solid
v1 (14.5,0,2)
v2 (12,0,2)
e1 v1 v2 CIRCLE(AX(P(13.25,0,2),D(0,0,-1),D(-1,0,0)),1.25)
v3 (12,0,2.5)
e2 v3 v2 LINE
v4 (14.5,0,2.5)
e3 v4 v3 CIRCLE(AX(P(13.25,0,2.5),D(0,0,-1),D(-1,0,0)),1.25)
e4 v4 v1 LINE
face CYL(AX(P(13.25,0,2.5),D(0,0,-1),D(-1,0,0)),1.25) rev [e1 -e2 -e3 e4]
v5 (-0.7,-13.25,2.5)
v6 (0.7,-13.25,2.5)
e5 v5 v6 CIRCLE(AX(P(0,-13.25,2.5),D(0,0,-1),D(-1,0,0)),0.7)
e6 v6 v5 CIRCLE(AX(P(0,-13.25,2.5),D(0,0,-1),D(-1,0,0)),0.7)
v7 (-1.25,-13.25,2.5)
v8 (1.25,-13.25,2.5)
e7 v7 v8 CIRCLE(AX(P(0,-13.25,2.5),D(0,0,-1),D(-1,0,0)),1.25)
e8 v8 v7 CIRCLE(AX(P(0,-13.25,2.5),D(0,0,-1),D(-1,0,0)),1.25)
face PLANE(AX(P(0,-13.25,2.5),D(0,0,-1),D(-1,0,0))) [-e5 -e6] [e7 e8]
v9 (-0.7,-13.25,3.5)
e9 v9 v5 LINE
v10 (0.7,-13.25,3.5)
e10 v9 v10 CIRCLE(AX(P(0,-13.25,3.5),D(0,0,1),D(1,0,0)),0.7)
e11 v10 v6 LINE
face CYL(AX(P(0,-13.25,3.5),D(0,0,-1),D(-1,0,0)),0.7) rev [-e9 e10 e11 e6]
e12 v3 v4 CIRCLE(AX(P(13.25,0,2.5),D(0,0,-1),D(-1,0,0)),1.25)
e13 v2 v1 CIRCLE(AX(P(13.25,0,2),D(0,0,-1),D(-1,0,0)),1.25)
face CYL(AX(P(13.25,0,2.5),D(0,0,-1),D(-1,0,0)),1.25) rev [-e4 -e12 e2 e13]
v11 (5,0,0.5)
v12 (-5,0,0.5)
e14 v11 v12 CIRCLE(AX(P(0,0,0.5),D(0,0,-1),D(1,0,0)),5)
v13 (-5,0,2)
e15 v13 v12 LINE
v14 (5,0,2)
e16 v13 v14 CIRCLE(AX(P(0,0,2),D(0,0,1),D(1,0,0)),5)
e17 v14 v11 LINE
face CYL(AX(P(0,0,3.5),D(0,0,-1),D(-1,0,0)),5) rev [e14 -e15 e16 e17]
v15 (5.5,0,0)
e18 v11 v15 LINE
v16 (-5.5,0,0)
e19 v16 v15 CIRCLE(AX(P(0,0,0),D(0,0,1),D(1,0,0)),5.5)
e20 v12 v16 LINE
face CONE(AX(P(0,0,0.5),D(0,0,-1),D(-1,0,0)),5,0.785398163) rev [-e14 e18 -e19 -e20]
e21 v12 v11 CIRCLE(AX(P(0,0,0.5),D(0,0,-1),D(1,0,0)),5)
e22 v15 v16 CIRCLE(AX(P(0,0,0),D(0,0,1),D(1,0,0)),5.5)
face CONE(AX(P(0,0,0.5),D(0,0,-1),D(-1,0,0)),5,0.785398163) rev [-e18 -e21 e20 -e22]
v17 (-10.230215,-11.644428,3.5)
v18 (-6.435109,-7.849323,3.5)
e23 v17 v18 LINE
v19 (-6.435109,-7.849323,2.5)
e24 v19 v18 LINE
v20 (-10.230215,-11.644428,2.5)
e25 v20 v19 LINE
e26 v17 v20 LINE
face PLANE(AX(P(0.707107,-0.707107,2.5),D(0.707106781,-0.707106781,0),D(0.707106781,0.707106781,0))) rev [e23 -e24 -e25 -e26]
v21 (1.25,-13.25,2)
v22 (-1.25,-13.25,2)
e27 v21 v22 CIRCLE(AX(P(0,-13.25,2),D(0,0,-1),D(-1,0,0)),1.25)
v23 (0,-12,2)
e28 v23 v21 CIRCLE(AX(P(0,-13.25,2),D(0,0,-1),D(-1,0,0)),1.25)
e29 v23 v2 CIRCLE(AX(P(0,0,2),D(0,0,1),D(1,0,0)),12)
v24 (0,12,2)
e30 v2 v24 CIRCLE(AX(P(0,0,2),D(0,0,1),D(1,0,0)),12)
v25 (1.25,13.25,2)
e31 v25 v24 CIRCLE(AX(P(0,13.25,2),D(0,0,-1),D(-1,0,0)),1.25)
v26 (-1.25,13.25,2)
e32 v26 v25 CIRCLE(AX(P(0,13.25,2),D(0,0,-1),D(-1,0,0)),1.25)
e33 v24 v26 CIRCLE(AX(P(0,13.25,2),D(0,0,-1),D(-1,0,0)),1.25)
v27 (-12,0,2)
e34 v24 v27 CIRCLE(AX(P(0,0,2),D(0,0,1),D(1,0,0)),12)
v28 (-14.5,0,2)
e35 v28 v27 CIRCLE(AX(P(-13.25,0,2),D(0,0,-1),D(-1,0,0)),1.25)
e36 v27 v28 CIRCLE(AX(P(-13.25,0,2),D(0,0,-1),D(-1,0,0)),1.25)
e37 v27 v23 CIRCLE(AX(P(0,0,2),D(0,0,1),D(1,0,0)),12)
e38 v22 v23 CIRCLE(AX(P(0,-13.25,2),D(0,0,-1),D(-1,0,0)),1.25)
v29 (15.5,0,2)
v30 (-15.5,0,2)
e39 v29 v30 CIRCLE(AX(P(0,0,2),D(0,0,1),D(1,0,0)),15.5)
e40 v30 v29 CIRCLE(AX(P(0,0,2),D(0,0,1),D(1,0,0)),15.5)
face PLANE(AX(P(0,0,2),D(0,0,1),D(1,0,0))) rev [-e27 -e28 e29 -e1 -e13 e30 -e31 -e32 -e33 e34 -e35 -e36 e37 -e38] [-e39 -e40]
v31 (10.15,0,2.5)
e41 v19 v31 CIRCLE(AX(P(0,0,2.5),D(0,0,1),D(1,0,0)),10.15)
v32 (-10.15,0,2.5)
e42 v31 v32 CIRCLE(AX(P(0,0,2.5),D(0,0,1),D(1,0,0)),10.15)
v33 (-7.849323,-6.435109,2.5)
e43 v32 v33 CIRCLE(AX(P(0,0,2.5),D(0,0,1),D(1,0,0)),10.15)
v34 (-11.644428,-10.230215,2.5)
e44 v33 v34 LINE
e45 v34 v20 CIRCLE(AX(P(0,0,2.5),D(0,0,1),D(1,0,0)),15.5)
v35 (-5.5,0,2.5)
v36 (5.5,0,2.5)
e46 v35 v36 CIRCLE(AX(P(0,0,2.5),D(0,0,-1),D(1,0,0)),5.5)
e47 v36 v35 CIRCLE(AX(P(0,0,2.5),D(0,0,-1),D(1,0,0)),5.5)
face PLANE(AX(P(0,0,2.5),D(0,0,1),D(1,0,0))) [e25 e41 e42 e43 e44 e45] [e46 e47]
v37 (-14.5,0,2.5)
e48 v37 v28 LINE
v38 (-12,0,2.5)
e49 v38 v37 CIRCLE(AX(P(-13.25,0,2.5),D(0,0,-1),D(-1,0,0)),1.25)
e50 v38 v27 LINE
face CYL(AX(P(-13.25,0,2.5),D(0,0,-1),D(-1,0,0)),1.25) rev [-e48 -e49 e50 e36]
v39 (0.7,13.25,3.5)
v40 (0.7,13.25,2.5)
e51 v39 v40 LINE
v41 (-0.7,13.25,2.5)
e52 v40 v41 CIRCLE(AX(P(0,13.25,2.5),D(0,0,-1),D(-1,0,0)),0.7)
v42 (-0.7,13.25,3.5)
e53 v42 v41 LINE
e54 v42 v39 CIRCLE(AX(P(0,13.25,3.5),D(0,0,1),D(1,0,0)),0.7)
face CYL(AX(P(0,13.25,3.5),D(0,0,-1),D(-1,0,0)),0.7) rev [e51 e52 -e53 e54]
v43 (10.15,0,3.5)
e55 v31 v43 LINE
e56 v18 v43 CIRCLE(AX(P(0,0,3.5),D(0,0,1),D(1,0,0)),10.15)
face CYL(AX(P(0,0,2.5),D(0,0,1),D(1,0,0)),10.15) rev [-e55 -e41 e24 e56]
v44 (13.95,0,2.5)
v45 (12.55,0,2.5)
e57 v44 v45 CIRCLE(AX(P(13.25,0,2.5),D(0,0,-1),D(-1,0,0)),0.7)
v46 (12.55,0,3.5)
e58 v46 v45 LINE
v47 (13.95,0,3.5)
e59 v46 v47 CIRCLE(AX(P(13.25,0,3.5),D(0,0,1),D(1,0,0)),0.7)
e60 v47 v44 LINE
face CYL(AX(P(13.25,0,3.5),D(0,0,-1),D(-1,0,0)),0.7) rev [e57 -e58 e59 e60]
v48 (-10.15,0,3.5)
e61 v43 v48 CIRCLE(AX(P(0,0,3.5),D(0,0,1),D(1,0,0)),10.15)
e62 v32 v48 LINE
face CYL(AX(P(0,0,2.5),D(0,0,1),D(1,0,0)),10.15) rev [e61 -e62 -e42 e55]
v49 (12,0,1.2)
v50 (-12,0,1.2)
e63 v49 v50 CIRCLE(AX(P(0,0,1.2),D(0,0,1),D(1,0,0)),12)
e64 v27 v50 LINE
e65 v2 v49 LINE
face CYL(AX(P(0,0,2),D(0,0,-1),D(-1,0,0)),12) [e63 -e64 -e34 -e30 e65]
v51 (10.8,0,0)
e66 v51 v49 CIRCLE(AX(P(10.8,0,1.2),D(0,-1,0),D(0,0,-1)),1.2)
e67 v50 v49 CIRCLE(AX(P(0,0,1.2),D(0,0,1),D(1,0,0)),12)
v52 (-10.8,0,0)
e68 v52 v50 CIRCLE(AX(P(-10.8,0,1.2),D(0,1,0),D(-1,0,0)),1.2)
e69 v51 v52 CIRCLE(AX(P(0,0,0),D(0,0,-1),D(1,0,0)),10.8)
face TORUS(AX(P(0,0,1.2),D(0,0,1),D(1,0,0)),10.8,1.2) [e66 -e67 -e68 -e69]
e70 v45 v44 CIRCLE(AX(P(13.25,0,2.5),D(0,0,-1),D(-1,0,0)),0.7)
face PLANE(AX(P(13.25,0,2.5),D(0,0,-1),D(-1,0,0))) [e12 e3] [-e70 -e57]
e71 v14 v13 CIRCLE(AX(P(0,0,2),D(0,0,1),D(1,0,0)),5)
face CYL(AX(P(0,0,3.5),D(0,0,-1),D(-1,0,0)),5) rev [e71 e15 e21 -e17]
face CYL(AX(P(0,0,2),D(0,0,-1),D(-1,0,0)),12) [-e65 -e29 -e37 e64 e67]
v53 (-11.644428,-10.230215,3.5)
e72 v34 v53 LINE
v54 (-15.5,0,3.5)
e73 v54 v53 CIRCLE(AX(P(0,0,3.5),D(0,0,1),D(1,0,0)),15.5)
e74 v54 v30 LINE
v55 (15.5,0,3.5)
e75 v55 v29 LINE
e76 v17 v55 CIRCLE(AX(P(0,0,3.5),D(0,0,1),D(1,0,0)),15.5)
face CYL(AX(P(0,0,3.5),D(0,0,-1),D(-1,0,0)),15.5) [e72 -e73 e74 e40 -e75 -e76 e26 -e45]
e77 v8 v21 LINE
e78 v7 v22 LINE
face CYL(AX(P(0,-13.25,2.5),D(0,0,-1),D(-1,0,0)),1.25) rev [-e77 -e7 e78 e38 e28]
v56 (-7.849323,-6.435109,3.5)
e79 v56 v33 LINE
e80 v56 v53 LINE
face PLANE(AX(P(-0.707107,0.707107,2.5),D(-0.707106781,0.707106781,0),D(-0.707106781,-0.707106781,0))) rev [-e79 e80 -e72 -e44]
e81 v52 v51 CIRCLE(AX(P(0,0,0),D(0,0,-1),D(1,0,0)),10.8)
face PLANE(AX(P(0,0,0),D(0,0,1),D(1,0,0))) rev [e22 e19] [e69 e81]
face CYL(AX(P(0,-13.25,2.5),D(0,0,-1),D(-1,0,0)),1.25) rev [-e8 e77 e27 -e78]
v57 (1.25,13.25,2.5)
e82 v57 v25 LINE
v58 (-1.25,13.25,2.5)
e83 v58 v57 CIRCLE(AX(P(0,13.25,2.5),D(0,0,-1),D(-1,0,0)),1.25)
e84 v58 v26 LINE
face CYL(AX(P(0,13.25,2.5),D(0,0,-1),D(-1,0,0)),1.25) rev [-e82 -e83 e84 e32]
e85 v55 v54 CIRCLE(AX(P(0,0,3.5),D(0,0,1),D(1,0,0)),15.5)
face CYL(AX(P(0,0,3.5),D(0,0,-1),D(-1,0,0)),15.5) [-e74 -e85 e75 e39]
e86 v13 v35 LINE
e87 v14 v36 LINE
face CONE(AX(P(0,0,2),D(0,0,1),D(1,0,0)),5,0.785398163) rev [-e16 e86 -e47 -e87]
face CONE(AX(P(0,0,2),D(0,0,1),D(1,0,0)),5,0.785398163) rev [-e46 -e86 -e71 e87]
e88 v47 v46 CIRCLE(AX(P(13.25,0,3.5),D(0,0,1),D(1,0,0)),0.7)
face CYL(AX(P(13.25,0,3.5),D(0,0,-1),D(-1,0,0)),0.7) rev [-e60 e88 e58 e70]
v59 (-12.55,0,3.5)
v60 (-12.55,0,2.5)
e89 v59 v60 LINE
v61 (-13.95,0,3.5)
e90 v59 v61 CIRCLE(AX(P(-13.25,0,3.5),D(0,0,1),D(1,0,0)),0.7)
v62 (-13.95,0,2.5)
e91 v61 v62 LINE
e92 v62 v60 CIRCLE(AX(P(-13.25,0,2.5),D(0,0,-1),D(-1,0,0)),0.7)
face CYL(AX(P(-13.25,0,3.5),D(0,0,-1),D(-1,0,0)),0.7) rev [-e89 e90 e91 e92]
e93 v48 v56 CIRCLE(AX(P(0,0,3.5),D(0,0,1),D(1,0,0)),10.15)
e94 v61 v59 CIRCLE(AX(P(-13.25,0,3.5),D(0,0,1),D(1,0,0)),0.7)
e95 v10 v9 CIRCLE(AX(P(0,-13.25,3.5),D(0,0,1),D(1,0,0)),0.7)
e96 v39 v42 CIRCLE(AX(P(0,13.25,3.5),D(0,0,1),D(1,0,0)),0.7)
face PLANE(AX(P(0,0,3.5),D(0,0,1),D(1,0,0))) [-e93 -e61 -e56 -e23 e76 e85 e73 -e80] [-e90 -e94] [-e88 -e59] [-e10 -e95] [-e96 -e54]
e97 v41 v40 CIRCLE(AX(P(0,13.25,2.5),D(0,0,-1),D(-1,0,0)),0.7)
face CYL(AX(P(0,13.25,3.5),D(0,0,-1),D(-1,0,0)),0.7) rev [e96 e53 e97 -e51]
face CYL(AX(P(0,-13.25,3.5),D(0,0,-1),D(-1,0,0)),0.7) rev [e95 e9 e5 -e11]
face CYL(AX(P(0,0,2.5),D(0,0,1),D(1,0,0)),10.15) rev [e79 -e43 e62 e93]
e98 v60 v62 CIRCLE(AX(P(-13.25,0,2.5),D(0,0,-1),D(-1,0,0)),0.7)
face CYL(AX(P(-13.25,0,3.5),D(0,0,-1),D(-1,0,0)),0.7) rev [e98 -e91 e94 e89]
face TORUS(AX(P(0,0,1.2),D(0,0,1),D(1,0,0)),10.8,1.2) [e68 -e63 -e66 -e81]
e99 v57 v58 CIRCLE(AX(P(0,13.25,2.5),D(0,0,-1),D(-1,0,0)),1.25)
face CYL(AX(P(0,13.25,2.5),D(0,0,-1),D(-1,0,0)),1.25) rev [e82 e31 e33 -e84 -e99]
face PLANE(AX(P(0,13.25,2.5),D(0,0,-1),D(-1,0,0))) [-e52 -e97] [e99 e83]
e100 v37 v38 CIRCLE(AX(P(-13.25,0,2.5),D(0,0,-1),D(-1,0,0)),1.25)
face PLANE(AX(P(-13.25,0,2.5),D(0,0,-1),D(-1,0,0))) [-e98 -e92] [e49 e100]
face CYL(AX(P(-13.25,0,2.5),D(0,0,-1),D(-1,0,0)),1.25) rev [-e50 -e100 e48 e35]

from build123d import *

# Parameters (mm, degrees)
SKETCH1_R           = 12
BOSS_EXTRUDE1_DEPTH = 2
SKETCH2_R           = 15.5
SKETCH2_R_2         = 0.7
BOSS_EXTRUDE2_DEPTH = 1.5
SKETCH3_R           = 10.15
CUT_EXTRUDE1_DEPTH  = 1
FILLET1_R           = 1.2
SKETCH4_R           = 1.25
CUT_EXTRUDE2_DEPTH  = 0.5
SKETCH5_R           = 5
CUT_EXTRUDE3_DEPTH  = 23.19797288
CHAMFER1_SIZE       = 0.5
CUT_EXTRUDE4_DEPTH  = 1


with BuildPart() as part:
    # Sketch1 → Boss-Extrude1 (new body)
    with BuildSketch(Plane.XY):
        Circle(SKETCH1_R)
    extrude(amount=BOSS_EXTRUDE1_DEPTH)

    # Sketch2 → Boss-Extrude2 (add)
    with BuildSketch(Plane.XY.offset(2)):
        Circle(SKETCH2_R)
        with Locations((0, 13.25)):
            Circle(SKETCH2_R_2, mode=Mode.SUBTRACT)
        with Locations((13.25, 0)):
            Circle(SKETCH2_R_2, mode=Mode.SUBTRACT)
        with Locations((0, -13.25)):
            Circle(SKETCH2_R_2, mode=Mode.SUBTRACT)
        with Locations((-13.25, 0)):
            Circle(SKETCH2_R_2, mode=Mode.SUBTRACT)
    extrude(amount=BOSS_EXTRUDE2_DEPTH)

    # Sketch3 → Cut-Extrude1 (cut)
    with BuildSketch(Plane.XY.offset(3.5)):
        Circle(SKETCH3_R)
    extrude(amount=-CUT_EXTRUDE1_DEPTH, mode=Mode.SUBTRACT)

    # Fillet1
    fillet1_edges = [part.edges().sort_by_distance(p)[0] for p in [
        (-12, 0, 0),
    ]]
    fillet(fillet1_edges, radius=FILLET1_R)

    # Sketch4 → Cut-Extrude2 (cut)
    with BuildSketch(Plane(origin=(0, 0, 2), x_dir=(-1, 0, 0), z_dir=(0, 0, -1))):
        with Locations((0, 13.25)):
            Circle(SKETCH4_R)
        with Locations((13.25, 0)):
            Circle(SKETCH4_R)
        with Locations((0, -13.25)):
            Circle(SKETCH4_R)
        with Locations((-13.25, 0)):
            Circle(SKETCH4_R)
    extrude(amount=-CUT_EXTRUDE2_DEPTH, mode=Mode.SUBTRACT)

    # Sketch5 → Cut-Extrude3 (cut, through all)
    with BuildSketch(Plane(origin=(0, 0, 0), x_dir=(-1, 0, 0), z_dir=(0, 0, -1))):
        Circle(SKETCH5_R)
    extrude(amount=-CUT_EXTRUDE3_DEPTH, mode=Mode.SUBTRACT)

    # Chamfer1
    chamfer1_edges = [part.edges().sort_by_distance(p)[0] for p in [
        (5, 0, 2.5),
        (5, 0, 0),
    ]]
    chamfer(chamfer1_edges, length=CHAMFER1_SIZE)

    # Sketch6 → Cut-Extrude4 (cut)
    with BuildSketch(Plane.XY.offset(3.5)):
        Polygon((-0.707106781, 0.707106781), (0.707106781, -0.707106781), (-10.253048327, -11.66726189), (-11.66726189, -10.253048327), align=None)
    extrude(amount=-CUT_EXTRUDE4_DEPTH, mode=Mode.SUBTRACT)


solid = part.part
